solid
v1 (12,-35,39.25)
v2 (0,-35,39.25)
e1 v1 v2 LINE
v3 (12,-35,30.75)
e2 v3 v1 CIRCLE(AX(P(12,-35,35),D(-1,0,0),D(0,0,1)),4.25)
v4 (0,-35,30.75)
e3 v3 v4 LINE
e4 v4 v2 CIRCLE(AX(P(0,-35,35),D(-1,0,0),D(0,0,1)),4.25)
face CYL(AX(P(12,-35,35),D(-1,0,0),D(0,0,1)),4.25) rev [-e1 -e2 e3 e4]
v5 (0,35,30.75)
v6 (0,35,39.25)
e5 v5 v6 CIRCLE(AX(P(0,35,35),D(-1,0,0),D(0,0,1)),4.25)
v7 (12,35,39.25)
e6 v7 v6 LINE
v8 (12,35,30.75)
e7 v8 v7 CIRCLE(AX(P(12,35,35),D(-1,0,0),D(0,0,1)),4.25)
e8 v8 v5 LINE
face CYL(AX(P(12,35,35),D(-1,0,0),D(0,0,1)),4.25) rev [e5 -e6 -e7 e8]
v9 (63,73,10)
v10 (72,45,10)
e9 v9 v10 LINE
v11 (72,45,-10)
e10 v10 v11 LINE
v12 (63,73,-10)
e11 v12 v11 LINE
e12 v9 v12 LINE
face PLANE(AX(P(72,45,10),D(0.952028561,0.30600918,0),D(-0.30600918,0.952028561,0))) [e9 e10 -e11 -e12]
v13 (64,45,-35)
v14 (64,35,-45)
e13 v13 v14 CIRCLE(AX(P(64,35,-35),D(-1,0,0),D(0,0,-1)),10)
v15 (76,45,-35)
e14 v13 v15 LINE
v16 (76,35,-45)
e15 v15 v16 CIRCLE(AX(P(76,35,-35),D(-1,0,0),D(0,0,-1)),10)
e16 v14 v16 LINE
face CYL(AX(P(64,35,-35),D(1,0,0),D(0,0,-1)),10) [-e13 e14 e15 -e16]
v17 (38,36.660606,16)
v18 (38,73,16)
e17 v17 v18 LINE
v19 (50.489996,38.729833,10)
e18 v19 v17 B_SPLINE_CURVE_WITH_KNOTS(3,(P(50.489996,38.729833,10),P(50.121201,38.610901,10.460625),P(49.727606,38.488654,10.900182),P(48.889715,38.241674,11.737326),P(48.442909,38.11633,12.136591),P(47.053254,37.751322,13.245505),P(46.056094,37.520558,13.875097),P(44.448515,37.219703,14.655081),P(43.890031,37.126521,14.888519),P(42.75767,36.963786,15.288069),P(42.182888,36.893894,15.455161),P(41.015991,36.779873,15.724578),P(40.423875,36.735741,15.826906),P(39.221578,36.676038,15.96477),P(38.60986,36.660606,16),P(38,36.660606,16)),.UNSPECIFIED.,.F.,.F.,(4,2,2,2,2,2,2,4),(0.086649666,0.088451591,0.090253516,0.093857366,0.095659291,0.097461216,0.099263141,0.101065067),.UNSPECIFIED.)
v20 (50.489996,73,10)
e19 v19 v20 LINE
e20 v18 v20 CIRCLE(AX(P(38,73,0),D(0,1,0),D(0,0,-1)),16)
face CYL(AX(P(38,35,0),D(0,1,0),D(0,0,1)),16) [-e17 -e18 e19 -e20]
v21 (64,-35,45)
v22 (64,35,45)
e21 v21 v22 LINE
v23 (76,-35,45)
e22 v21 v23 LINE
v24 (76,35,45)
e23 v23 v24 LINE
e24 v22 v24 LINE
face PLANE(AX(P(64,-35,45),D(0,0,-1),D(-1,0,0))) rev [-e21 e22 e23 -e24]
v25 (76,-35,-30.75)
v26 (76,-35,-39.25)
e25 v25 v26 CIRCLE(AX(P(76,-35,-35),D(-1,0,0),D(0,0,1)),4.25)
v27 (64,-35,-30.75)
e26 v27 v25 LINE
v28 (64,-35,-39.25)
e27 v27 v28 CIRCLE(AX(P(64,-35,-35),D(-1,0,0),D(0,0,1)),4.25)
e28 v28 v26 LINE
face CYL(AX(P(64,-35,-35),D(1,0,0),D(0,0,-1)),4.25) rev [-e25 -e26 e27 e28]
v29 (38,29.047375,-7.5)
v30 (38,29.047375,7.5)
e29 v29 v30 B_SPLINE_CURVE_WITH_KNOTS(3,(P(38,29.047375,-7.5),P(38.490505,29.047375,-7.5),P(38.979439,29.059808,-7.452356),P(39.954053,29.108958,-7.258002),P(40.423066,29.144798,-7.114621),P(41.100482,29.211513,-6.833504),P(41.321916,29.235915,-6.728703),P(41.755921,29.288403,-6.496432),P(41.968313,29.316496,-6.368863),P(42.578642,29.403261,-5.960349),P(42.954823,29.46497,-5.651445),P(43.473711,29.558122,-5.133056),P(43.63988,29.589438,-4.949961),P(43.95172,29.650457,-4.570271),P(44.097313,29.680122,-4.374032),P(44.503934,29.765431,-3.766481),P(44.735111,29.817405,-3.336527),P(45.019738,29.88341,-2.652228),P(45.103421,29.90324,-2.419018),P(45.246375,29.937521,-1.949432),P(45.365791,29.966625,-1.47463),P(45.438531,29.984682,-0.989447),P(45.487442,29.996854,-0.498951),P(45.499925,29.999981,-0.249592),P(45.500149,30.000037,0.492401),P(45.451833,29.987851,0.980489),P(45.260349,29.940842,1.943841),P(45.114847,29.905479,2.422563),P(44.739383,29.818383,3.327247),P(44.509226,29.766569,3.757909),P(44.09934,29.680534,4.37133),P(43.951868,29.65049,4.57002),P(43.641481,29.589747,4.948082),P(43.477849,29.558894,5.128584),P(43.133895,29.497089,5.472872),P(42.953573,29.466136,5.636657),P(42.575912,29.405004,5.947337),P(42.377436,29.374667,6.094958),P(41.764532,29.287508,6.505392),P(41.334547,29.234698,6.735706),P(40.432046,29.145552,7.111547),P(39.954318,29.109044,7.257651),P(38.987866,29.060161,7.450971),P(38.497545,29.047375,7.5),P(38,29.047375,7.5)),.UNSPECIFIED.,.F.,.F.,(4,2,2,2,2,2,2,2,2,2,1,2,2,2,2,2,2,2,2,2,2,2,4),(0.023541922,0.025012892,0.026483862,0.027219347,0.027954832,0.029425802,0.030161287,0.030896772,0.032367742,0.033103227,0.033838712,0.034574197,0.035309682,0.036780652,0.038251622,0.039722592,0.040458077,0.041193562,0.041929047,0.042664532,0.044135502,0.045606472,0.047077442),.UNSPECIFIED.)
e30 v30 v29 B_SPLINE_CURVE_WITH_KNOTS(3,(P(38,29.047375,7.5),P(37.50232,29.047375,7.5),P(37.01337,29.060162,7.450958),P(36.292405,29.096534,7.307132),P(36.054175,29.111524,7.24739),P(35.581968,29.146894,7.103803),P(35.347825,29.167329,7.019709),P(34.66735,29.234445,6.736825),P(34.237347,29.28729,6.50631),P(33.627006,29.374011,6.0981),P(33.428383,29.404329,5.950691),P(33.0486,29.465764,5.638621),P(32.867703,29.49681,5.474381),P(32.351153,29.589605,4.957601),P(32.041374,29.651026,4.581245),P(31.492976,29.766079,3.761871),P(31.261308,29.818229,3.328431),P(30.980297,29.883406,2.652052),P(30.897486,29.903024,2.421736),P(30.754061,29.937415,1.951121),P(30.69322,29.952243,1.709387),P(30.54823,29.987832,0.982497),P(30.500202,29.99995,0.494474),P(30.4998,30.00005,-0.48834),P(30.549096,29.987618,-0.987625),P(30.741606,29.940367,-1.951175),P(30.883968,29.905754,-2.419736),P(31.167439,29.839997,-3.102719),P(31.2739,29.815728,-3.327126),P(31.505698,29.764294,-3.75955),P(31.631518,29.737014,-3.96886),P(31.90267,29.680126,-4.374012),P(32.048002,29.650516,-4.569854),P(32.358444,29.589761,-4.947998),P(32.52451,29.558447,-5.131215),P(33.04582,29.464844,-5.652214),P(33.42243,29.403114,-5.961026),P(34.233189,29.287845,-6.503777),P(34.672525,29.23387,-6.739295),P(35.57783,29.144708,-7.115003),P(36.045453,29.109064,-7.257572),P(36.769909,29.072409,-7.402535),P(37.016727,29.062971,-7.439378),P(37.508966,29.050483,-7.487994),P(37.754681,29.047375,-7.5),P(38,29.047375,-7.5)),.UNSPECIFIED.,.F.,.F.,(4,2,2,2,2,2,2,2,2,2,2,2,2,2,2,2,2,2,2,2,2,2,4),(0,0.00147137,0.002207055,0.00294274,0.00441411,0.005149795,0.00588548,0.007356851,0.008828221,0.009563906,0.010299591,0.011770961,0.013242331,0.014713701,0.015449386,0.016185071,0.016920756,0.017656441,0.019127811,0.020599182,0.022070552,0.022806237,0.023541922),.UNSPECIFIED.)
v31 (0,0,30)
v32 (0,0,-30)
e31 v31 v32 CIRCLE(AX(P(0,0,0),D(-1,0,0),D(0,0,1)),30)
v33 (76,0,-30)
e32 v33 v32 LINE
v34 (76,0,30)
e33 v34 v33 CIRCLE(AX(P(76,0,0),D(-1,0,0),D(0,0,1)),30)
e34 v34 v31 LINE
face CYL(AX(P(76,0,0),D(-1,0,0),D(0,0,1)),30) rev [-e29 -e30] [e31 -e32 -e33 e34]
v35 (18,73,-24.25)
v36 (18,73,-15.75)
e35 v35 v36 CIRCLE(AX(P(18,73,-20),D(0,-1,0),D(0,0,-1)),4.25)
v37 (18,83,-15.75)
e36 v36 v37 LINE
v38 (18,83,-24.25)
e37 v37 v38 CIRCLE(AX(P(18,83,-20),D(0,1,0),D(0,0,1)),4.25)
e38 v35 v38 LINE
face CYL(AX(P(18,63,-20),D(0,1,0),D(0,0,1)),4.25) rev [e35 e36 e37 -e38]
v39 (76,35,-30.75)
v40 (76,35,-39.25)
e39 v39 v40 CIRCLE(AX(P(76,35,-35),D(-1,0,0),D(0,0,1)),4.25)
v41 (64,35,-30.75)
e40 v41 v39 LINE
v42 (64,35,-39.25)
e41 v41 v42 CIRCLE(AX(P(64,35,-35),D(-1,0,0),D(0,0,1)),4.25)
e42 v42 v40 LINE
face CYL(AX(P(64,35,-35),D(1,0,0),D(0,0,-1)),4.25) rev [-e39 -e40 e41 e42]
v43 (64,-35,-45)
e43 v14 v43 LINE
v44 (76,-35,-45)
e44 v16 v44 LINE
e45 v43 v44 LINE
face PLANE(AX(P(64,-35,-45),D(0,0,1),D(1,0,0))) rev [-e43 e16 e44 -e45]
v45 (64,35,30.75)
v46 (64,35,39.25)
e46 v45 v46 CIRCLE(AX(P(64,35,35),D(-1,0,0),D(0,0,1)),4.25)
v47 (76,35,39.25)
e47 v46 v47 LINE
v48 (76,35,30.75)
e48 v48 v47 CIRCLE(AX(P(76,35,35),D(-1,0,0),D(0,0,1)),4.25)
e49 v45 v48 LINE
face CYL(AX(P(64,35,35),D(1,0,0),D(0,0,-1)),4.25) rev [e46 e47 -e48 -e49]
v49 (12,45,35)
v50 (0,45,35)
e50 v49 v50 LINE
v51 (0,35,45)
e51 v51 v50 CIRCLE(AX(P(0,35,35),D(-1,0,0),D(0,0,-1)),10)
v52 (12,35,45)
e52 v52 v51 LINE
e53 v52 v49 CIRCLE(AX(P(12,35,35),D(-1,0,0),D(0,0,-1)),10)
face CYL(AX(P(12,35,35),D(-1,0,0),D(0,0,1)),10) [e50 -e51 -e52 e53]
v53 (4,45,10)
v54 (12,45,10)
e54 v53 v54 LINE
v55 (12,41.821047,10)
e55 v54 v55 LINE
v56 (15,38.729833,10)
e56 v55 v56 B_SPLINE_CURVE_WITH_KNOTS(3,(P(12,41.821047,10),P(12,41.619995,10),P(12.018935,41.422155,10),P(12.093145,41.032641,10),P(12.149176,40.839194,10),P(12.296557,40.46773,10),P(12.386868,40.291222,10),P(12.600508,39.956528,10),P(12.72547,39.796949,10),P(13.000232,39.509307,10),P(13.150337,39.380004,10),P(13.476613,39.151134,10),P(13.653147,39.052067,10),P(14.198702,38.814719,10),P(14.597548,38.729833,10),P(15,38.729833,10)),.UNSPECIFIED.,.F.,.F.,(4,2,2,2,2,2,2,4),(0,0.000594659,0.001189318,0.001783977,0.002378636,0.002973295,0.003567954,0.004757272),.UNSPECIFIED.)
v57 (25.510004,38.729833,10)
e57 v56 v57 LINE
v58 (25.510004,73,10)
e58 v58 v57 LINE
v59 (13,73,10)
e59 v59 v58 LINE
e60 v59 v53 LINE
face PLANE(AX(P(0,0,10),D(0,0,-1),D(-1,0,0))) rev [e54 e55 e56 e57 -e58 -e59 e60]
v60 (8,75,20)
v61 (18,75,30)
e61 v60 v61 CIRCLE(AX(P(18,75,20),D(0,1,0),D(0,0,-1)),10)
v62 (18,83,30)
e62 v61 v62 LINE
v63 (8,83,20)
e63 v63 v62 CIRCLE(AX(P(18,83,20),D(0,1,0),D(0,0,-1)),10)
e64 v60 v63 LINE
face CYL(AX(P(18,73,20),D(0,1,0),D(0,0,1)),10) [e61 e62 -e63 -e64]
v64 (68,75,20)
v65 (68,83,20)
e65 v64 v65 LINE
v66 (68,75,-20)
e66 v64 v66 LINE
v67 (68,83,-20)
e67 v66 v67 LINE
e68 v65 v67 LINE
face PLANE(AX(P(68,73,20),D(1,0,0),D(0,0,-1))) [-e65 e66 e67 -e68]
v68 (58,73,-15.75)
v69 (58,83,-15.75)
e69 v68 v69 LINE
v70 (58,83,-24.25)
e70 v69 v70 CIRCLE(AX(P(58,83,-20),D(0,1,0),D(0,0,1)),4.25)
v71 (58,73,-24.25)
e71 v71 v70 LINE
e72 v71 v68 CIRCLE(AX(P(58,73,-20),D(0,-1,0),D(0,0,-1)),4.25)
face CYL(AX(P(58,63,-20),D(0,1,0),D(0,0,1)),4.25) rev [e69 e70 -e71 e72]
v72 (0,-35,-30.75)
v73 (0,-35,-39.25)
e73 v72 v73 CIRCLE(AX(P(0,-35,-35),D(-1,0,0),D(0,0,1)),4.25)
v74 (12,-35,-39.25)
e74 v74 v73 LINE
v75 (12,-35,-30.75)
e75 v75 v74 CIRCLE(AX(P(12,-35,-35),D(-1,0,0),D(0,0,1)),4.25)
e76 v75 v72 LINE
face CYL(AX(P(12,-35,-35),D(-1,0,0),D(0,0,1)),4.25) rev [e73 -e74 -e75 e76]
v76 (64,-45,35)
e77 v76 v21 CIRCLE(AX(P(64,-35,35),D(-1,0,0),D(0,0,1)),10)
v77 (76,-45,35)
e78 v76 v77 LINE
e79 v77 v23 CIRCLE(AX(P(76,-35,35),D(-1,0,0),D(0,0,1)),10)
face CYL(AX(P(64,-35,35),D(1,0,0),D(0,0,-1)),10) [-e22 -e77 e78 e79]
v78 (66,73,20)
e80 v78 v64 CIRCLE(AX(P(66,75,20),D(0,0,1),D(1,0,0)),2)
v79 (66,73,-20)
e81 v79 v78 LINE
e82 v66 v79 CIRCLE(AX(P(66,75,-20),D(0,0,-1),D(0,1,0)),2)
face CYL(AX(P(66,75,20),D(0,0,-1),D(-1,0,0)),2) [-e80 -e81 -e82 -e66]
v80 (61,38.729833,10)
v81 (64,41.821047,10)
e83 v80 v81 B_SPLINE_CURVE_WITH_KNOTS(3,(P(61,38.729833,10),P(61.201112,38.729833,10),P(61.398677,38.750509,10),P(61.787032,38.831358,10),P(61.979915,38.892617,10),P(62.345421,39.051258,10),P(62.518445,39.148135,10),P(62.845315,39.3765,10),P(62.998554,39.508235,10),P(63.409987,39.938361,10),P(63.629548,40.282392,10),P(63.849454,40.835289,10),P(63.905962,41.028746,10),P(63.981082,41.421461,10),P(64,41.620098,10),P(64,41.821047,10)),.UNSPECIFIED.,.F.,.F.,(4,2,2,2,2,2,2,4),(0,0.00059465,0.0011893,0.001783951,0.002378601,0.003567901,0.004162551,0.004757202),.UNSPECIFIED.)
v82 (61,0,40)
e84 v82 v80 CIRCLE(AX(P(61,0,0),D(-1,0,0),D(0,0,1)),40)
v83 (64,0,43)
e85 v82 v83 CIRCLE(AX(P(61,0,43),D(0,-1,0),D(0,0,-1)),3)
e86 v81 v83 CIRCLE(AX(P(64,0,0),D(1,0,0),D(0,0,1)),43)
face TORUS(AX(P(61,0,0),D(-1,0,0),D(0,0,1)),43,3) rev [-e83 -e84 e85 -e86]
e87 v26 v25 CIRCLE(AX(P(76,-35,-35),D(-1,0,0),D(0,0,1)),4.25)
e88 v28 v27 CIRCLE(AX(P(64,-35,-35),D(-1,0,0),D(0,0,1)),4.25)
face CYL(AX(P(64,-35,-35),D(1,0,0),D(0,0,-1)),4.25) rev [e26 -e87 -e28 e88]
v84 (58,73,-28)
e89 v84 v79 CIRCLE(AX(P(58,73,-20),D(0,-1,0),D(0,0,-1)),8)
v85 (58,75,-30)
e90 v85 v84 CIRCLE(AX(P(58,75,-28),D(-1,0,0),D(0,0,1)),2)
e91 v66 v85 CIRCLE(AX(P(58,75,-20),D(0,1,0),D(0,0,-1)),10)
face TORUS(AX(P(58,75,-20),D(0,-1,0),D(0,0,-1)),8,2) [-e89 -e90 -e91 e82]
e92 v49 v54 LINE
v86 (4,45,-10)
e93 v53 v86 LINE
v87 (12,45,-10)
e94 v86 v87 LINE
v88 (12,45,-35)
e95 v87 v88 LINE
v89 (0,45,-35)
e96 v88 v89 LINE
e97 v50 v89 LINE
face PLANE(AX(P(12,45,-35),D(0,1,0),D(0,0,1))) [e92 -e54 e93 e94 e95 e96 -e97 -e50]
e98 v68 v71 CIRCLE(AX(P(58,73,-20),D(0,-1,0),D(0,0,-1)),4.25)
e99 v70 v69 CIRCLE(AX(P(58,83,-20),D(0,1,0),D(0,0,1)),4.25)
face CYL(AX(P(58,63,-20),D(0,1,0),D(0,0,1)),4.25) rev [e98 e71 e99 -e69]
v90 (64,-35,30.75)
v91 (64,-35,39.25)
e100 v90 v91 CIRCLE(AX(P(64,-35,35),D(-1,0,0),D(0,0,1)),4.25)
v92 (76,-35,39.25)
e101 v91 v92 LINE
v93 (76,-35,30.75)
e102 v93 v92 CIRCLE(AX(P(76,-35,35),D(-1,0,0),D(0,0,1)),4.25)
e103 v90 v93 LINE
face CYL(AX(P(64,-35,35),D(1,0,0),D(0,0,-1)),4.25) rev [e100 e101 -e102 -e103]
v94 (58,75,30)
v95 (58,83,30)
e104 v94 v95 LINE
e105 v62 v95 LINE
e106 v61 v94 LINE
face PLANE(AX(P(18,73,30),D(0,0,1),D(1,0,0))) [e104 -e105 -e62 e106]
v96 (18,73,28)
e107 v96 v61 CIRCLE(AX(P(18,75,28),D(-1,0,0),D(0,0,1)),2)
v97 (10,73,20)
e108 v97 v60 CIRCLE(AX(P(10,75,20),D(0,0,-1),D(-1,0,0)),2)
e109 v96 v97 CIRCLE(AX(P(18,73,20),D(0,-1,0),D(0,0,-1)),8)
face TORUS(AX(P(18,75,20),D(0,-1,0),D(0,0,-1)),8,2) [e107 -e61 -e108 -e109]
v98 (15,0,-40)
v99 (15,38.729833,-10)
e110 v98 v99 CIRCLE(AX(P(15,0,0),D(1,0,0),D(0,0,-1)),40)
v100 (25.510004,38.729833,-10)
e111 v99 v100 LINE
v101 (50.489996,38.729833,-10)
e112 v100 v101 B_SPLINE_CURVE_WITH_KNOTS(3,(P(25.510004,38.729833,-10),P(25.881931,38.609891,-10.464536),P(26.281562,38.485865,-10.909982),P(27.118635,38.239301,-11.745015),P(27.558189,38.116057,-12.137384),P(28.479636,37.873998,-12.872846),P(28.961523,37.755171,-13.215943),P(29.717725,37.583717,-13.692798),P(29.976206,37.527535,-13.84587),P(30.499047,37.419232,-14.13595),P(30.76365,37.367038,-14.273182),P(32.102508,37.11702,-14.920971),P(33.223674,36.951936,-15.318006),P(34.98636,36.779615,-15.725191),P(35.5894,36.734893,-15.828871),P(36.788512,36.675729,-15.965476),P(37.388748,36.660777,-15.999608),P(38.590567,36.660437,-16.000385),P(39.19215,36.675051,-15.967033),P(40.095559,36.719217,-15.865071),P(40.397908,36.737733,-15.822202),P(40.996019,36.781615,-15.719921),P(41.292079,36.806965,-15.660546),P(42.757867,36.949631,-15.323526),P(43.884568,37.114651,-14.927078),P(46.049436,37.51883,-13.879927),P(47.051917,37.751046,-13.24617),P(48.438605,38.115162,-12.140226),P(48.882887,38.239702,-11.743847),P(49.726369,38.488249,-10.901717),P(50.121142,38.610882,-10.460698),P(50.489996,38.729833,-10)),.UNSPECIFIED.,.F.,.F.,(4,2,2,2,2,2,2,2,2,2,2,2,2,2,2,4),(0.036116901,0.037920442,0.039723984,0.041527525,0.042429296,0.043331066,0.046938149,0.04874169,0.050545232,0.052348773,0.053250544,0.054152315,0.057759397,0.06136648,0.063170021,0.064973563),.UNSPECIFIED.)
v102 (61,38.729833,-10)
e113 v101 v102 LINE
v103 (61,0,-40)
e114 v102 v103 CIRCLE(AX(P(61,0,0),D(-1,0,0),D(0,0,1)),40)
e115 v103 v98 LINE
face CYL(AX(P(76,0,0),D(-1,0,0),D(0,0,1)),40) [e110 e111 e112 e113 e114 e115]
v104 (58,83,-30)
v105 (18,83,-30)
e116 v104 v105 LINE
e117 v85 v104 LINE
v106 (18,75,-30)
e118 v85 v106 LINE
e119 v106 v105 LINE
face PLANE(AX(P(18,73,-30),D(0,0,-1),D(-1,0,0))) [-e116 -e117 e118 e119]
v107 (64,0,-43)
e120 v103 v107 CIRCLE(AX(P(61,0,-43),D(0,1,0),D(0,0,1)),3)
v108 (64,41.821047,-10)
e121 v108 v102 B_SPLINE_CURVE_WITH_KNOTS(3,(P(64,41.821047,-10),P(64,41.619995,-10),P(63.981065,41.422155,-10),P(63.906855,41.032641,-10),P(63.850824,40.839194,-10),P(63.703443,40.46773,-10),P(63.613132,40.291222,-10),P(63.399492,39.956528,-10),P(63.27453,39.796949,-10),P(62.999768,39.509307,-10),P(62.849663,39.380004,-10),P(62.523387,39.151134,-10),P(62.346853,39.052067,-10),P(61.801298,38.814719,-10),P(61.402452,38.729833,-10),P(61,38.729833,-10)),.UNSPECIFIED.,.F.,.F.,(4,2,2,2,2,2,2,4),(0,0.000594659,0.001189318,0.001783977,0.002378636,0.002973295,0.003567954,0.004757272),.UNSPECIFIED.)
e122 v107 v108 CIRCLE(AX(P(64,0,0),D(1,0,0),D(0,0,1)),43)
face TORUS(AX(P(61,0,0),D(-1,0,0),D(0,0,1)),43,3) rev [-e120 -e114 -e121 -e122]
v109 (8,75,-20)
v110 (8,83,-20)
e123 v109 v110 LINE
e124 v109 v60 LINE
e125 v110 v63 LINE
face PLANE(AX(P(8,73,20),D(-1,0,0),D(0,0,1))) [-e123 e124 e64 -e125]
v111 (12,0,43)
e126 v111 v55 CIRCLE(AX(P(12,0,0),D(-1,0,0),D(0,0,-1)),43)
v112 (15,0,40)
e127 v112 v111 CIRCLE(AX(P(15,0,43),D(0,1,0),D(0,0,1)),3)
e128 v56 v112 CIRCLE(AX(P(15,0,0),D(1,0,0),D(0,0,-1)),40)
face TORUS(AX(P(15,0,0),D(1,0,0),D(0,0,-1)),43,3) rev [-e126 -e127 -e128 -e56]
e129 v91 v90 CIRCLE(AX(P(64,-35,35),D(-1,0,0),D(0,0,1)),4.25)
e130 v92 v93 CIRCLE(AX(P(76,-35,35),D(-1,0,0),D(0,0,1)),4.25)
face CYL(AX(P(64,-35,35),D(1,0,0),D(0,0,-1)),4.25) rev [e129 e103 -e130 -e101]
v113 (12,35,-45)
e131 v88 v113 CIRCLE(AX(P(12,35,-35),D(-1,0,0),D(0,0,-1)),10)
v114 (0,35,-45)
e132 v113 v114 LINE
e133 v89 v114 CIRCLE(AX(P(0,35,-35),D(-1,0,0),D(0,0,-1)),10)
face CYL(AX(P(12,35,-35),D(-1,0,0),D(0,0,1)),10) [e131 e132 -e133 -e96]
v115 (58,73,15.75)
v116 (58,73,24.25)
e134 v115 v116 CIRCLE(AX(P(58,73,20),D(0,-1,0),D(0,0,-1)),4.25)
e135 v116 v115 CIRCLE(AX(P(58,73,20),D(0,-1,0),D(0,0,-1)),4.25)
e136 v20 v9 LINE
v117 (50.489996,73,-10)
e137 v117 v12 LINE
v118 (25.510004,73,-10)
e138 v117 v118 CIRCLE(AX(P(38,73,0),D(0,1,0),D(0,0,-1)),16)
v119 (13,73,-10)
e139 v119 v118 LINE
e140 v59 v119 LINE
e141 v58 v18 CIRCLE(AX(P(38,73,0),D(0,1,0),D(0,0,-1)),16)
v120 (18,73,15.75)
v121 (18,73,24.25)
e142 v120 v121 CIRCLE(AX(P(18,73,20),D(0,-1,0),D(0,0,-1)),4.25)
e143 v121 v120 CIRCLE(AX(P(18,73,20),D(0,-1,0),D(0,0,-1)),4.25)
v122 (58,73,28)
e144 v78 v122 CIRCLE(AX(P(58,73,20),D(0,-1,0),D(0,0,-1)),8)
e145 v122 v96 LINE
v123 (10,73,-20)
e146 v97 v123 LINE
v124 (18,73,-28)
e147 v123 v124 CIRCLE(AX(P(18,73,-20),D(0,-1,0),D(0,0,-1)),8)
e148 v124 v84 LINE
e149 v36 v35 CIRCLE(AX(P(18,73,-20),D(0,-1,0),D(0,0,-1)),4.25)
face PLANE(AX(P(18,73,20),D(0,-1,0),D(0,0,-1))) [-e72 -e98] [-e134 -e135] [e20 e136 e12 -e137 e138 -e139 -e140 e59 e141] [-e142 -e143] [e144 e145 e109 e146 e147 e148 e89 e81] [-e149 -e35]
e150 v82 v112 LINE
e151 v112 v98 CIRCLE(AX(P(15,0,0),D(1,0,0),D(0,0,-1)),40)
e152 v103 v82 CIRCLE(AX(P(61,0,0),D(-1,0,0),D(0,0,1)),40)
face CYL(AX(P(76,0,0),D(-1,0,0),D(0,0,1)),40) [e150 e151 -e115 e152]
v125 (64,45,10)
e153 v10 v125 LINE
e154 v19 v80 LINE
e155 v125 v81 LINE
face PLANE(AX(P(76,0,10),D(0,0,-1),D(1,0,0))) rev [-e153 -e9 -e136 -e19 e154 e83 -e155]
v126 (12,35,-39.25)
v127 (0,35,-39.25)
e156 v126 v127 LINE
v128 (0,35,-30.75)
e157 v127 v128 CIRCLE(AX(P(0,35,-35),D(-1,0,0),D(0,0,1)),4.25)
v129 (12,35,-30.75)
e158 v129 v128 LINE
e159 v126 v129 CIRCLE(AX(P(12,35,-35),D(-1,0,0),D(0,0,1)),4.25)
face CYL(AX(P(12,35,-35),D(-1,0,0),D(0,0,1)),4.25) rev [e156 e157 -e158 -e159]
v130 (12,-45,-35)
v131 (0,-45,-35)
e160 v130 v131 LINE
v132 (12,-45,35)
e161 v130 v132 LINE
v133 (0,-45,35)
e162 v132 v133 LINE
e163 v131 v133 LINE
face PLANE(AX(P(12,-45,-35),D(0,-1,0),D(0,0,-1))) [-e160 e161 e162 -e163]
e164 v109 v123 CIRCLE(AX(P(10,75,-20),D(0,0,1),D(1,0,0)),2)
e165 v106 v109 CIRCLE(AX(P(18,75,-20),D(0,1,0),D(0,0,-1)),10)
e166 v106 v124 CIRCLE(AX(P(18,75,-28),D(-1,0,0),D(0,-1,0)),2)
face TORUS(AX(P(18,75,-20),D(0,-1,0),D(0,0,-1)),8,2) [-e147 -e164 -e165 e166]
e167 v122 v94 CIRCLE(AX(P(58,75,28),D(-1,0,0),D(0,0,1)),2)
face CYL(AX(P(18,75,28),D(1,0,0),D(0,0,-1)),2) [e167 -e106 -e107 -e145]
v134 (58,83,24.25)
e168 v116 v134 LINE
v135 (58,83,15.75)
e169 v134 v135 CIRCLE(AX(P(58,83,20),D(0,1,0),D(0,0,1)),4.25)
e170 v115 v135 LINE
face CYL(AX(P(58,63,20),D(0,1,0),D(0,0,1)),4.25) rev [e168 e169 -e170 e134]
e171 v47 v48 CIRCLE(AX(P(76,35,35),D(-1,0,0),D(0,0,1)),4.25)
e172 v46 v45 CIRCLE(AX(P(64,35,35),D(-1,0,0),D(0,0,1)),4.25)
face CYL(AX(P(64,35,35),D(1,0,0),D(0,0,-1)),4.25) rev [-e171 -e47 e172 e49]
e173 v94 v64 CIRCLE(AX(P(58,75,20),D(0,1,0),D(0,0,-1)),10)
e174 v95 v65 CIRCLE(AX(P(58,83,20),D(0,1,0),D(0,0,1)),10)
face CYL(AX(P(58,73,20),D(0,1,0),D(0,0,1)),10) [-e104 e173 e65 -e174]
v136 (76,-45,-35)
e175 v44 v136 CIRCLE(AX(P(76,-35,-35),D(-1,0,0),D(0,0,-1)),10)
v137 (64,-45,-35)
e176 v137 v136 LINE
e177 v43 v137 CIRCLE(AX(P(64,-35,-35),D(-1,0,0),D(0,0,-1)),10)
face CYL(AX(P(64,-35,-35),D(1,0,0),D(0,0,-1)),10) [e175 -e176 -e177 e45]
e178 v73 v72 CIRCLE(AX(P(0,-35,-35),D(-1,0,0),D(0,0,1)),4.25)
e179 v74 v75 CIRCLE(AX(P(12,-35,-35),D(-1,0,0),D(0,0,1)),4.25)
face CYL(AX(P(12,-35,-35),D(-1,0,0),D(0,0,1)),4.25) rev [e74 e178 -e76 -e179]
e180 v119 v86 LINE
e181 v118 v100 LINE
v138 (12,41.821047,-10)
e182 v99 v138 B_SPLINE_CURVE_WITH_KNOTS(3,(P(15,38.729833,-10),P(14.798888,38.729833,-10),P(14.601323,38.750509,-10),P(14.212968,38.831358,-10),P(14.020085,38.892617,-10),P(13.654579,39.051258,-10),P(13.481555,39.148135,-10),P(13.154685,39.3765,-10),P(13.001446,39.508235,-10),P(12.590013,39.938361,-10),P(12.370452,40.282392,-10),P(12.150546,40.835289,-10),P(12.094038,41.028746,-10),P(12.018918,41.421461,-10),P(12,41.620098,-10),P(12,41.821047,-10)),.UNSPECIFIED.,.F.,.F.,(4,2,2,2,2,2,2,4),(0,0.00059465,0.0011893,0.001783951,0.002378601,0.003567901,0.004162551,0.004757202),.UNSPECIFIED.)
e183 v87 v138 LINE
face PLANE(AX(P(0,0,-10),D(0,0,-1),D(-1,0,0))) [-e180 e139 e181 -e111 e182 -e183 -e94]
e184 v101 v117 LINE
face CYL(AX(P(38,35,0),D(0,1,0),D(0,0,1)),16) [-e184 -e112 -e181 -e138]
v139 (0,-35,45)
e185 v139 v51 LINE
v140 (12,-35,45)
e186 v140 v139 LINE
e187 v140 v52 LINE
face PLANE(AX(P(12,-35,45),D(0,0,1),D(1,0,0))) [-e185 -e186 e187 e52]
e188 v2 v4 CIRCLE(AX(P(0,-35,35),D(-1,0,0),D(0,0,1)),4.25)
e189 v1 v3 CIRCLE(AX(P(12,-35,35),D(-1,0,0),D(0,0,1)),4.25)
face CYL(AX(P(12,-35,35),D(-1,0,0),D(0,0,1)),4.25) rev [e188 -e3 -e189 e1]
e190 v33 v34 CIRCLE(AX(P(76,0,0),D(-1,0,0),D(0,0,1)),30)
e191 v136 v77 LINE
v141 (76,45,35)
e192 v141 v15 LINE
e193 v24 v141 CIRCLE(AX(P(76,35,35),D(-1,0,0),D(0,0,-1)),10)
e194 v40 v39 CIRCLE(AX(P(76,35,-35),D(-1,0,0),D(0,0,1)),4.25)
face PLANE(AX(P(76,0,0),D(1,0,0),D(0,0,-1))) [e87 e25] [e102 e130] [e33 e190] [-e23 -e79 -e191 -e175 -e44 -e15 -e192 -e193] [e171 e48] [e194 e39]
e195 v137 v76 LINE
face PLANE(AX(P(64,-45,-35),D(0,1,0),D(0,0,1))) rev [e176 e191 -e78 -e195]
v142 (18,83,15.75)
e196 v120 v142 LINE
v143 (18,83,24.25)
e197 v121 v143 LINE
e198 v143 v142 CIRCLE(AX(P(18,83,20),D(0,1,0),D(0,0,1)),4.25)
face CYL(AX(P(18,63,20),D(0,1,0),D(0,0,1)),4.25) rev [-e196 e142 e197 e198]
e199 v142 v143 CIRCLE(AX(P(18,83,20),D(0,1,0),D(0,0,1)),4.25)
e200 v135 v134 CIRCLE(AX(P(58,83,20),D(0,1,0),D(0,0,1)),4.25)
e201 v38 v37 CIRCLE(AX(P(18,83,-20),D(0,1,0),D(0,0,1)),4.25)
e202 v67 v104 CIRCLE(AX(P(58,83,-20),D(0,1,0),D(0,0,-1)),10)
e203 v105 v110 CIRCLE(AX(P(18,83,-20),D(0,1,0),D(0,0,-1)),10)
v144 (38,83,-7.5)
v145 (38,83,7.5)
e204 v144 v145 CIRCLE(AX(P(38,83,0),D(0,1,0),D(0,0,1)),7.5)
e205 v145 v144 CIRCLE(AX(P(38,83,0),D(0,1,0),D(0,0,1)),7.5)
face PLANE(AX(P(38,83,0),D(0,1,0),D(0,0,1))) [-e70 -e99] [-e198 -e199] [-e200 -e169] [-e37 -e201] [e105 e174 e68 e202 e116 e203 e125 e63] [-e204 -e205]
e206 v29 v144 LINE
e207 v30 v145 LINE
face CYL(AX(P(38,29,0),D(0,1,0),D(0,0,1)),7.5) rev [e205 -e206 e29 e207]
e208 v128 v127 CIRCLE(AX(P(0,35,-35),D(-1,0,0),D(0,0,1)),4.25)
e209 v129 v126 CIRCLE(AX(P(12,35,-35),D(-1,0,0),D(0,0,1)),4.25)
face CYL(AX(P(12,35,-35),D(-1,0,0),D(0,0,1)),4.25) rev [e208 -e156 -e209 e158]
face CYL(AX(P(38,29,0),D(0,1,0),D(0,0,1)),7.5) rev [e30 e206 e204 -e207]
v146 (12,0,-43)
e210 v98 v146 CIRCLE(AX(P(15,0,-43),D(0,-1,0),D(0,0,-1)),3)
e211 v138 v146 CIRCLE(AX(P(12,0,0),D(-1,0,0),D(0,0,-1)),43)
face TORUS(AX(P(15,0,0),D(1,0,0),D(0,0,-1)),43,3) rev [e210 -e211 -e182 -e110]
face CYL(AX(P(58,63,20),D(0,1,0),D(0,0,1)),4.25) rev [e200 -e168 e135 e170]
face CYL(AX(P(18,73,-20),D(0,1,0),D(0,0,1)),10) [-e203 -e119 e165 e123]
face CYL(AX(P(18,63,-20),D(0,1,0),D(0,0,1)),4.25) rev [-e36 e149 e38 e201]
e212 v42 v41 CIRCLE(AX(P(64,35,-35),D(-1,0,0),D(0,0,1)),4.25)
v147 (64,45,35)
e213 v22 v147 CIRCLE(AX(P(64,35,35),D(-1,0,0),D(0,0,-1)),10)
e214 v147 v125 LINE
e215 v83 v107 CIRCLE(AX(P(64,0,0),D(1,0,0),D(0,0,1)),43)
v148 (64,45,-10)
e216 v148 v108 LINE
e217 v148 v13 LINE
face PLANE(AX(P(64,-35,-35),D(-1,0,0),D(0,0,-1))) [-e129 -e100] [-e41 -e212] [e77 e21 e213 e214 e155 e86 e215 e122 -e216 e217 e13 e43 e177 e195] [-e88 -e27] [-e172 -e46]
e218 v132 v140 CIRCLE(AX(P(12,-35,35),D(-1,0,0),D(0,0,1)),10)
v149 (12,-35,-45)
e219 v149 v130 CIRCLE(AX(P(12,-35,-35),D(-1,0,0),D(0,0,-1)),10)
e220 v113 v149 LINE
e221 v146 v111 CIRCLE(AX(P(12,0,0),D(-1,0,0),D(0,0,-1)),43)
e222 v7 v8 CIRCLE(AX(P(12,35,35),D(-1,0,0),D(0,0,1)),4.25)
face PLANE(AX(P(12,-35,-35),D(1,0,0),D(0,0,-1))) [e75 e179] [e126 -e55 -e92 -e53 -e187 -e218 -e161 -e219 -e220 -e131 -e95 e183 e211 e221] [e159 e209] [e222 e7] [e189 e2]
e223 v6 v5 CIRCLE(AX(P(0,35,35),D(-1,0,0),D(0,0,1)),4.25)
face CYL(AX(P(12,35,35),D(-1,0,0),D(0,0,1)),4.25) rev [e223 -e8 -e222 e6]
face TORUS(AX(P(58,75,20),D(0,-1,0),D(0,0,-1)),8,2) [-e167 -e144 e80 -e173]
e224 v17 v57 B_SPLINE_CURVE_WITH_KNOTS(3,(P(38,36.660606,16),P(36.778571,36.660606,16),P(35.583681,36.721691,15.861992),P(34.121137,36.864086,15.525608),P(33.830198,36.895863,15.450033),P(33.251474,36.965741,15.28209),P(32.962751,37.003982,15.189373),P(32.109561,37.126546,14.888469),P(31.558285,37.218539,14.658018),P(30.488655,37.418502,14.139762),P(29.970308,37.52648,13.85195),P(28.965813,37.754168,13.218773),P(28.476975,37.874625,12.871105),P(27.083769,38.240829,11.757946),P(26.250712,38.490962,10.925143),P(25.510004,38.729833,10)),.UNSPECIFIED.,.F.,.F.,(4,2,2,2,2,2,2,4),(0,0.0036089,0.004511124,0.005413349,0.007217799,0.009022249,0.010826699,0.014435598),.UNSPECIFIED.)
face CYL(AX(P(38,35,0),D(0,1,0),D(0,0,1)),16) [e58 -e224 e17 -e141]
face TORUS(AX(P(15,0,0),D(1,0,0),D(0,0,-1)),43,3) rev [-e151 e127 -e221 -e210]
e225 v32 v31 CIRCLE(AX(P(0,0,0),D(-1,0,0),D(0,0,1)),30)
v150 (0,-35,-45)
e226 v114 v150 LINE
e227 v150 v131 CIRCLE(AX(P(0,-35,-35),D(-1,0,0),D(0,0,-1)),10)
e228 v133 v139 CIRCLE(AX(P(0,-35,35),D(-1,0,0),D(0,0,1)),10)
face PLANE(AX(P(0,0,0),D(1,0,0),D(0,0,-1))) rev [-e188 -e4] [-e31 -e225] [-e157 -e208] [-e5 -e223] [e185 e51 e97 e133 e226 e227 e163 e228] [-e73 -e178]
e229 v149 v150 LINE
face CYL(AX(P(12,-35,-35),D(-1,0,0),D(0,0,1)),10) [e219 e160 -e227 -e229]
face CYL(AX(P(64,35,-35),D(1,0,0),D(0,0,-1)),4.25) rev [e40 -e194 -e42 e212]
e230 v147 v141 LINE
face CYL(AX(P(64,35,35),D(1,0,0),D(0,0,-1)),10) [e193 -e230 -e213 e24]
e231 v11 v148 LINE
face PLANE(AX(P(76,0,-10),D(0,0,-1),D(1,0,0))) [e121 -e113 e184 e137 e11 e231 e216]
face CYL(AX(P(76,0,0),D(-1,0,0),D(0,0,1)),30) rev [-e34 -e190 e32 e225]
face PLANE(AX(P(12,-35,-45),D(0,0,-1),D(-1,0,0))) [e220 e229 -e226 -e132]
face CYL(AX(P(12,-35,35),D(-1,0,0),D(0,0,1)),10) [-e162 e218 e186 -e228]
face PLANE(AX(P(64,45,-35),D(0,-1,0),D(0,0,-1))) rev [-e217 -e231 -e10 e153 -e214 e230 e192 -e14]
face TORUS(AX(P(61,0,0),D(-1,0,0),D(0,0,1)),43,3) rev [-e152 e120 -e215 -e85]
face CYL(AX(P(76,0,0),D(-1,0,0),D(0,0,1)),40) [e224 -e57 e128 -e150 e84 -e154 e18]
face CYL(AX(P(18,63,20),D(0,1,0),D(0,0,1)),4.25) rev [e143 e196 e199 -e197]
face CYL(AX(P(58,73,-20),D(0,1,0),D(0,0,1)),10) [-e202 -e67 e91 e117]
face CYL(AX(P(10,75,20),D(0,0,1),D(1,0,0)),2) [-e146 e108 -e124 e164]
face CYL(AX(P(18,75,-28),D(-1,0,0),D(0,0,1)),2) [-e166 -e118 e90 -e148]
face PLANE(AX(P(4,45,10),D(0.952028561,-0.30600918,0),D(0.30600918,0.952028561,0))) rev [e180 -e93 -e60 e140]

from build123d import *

# Parameters (mm, degrees)
BODY_TUBE_SKETCH_R                 = 40
BODY_TUBE_SKETCH_R_2               = 30
BODY_TUBE_DEPTH                    = 76
END_FLANGE_DEPTH                   = 12
BODY_BORE_SKETCH_R                 = 30
BODY_BORE_60_DEPTH                 = 100.126182212
END_FLANGE_BOLT_HOLES_SKETCH_R     = 4.25
END_FLANGE_BOLT_HOLES_4X_8_5_DEPTH = 12
TOP_FLANGE_DEPTH                   = 10
STEM_NECK_SKETCH_R                 = 16
STEM_NECK_32_DEPTH                 = 48
NECK_SUPPORT_RIB_DEPTH             = 10
TOP_FLANGE_BOLT_HOLES_SKETCH_R     = 4.25
TOP_FLANGE_BOLT_HOLES_4X_8_5_DEPTH = 20
STEM_BORE_SKETCH_R                 = 7.5
STEM_BORE_15_DEPTH                 = 54
END_FLANGE_FILLETS_R3_R            = 3
TOP_FLANGE_FILLETS_R2_R            = 2


with BuildPart() as part:
    # Body Tube Sketch → Body Tube (new body)
    with BuildSketch(Plane(origin=(0, 0, 0), x_dir=(0, 0, -1), z_dir=(1, 0, 0))):
        Circle(BODY_TUBE_SKETCH_R)
        Circle(BODY_TUBE_SKETCH_R_2, mode=Mode.SUBTRACT)
    extrude(amount=BODY_TUBE_DEPTH)

    # End Flange Sketch → End Flange (add)
    with BuildSketch(Plane.ZY):
        with BuildLine():
            Line((-35, -45), (35, -45))
            ThreePointArc((35, -45), (42.071067812, -42.071067812), (45, -35))
            Line((45, -35), (45, 35))
            ThreePointArc((45, 35), (42.071067812, 42.071067812), (35, 45))
            Line((35, 45), (-35, 45))
            ThreePointArc((-35, 45), (-42.071067812, 42.071067812), (-45, 35))
            Line((-45, 35), (-45, -35))
            ThreePointArc((-45, -35), (-42.071067812, -42.071067812), (-35, -45))
        make_face()
    end_flange = extrude(amount=-END_FLANGE_DEPTH)

    # Body Bore Sketch → Body Bore Ø60 (cut, through all)
    with BuildSketch(Plane.ZY):
        Circle(BODY_BORE_SKETCH_R)
    body_bore_60 = extrude(amount=-BODY_BORE_60_DEPTH, mode=Mode.SUBTRACT)

    # End Flange Bolt Holes Sketch → End Flange Bolt Holes 4xØ8.5 (cut)
    with BuildSketch(Plane.ZY):
        with Locations((-35, 35)):
            Circle(END_FLANGE_BOLT_HOLES_SKETCH_R)
        with Locations((35, 35)):
            Circle(END_FLANGE_BOLT_HOLES_SKETCH_R)
        with Locations((-35, -35)):
            Circle(END_FLANGE_BOLT_HOLES_SKETCH_R)
        with Locations((35, -35)):
            Circle(END_FLANGE_BOLT_HOLES_SKETCH_R)
    end_flange_bolt_holes_4x_8_5 = extrude(amount=-END_FLANGE_BOLT_HOLES_4X_8_5_DEPTH, mode=Mode.SUBTRACT)

    # Opposite End Flange Mirror: End Flange across plane
    add(end_flange.mirror(Plane(origin=(38, 0, 0), x_dir=(0, 0, 1), z_dir=(1, 0, 0))))

    # Opposite Flange Holes and Bore Mirror: Body Bore Ø60, End Flange Bolt Holes 4xØ8.5 across plane
    add(body_bore_60.mirror(Plane(origin=(38, 0, 0), x_dir=(0, 0, 1), z_dir=(1, 0, 0))), mode=Mode.SUBTRACT)
    add(end_flange_bolt_holes_4x_8_5.mirror(Plane(origin=(38, 0, 0), x_dir=(0, 0, 1), z_dir=(1, 0, 0))), mode=Mode.SUBTRACT)



with BuildPart() as body_2:
    # Top Flange Sketch → Top Flange (new body)
    with BuildSketch(Plane(origin=(0, 83, 0), x_dir=(1, 0, 0), z_dir=(0, 1, 0))):
        with BuildLine():
            Line((18, -30), (58, -30))
            ThreePointArc((58, -30), (65.071067812, -27.071067812), (68, -20))
            Line((68, -20), (68, 20))
            ThreePointArc((68, 20), (65.071067812, 27.071067812), (58, 30))
            Line((58, 30), (18, 30))
            ThreePointArc((18, 30), (10.928932188, 27.071067812), (8, 20))
            Line((8, 20), (8, -20))
            ThreePointArc((8, -20), (10.928932188, -27.071067812), (18, -30))
        make_face()
    extrude(amount=-TOP_FLANGE_DEPTH)


with BuildPart() as part_1:
    add(part.part)

    add(body_2.part)  # Stem Neck Ø32 merges body 2
    # Stem Neck Sketch → Stem Neck Ø32 (add)
    with BuildSketch(Plane(origin=(0, 83, 0), x_dir=(1, 0, 0), z_dir=(0, 1, 0))):
        with Locations(Location((38, 0, 0), (0, 0, 270))):
            Circle(STEM_NECK_SKETCH_R)
    extrude(amount=-STEM_NECK_32_DEPTH)

    # Neck Support Rib Sketch → Neck Support Rib (add, symmetric)
    with BuildSketch(Plane.XY):
        Polygon((27.229131896, 73), (27.229131896, 33), (12, 33), (12, 45), (4, 45), (13, 73), align=None)
    neck_support_rib = extrude(amount=NECK_SUPPORT_RIB_DEPTH, both=True)

    # Neck Support Rib Mirror: Neck Support Rib across plane
    add(neck_support_rib.mirror(Plane(origin=(38, 0, 0), x_dir=(0, 0, 1), z_dir=(1, 0, 0))))

    # Top Flange Bolt Holes Sketch → Top Flange Bolt Holes 4xØ8.5 (cut)
    with BuildSketch(Plane(origin=(0, 83, 0), x_dir=(1, 0, 0), z_dir=(0, 1, 0))):
        with Locations(Location((18, 20, 0), (0, 0, 270))):
            Circle(TOP_FLANGE_BOLT_HOLES_SKETCH_R)
        with Locations(Location((58, 20, 0), (0, 0, 270))):
            Circle(TOP_FLANGE_BOLT_HOLES_SKETCH_R)
        with Locations(Location((18, -20, 0), (0, 0, 270))):
            Circle(TOP_FLANGE_BOLT_HOLES_SKETCH_R)
        with Locations(Location((58, -20, 0), (0, 0, 270))):
            Circle(TOP_FLANGE_BOLT_HOLES_SKETCH_R)
    extrude(amount=-TOP_FLANGE_BOLT_HOLES_4X_8_5_DEPTH, mode=Mode.SUBTRACT)

    # Stem Bore Sketch → Stem Bore Ø15 (cut)
    with BuildSketch(Plane(origin=(0, 83, 0), x_dir=(1, 0, 0), z_dir=(0, 1, 0))):
        with Locations(Location((38, 0, 0), (0, 0, 270))):
            Circle(STEM_BORE_SKETCH_R)
    extrude(amount=-STEM_BORE_15_DEPTH, mode=Mode.SUBTRACT)

    # End Flange Fillets R3
    end_flange_fillets_r3_edges = [part_1.edges().sort_by_distance(p)[0] for p in [
        (12, -31.622776602, 24.494897428),
        (64, -31.622776602, 24.494897428),
    ]]
    fillet(end_flange_fillets_r3_edges, radius=END_FLANGE_FILLETS_R3_R)

    # Top Flange Fillets R2
    top_flange_fillets_r2_edges = [part_1.edges().sort_by_distance(p)[0] for p in [
        (10.928932188, 73, 27.071067812),
        (8, 73, 0),
        (10.928932188, 73, -27.071067812),
        (38, 73, -30),
        (65.071067812, 73, -27.071067812),
        (68, 73, 0),
        (65.071067812, 73, 27.071067812),
        (38, 73, 30),
    ]]
    fillet(top_flange_fillets_r2_edges, radius=TOP_FLANGE_FILLETS_R2_R)


solid = part_1.part
